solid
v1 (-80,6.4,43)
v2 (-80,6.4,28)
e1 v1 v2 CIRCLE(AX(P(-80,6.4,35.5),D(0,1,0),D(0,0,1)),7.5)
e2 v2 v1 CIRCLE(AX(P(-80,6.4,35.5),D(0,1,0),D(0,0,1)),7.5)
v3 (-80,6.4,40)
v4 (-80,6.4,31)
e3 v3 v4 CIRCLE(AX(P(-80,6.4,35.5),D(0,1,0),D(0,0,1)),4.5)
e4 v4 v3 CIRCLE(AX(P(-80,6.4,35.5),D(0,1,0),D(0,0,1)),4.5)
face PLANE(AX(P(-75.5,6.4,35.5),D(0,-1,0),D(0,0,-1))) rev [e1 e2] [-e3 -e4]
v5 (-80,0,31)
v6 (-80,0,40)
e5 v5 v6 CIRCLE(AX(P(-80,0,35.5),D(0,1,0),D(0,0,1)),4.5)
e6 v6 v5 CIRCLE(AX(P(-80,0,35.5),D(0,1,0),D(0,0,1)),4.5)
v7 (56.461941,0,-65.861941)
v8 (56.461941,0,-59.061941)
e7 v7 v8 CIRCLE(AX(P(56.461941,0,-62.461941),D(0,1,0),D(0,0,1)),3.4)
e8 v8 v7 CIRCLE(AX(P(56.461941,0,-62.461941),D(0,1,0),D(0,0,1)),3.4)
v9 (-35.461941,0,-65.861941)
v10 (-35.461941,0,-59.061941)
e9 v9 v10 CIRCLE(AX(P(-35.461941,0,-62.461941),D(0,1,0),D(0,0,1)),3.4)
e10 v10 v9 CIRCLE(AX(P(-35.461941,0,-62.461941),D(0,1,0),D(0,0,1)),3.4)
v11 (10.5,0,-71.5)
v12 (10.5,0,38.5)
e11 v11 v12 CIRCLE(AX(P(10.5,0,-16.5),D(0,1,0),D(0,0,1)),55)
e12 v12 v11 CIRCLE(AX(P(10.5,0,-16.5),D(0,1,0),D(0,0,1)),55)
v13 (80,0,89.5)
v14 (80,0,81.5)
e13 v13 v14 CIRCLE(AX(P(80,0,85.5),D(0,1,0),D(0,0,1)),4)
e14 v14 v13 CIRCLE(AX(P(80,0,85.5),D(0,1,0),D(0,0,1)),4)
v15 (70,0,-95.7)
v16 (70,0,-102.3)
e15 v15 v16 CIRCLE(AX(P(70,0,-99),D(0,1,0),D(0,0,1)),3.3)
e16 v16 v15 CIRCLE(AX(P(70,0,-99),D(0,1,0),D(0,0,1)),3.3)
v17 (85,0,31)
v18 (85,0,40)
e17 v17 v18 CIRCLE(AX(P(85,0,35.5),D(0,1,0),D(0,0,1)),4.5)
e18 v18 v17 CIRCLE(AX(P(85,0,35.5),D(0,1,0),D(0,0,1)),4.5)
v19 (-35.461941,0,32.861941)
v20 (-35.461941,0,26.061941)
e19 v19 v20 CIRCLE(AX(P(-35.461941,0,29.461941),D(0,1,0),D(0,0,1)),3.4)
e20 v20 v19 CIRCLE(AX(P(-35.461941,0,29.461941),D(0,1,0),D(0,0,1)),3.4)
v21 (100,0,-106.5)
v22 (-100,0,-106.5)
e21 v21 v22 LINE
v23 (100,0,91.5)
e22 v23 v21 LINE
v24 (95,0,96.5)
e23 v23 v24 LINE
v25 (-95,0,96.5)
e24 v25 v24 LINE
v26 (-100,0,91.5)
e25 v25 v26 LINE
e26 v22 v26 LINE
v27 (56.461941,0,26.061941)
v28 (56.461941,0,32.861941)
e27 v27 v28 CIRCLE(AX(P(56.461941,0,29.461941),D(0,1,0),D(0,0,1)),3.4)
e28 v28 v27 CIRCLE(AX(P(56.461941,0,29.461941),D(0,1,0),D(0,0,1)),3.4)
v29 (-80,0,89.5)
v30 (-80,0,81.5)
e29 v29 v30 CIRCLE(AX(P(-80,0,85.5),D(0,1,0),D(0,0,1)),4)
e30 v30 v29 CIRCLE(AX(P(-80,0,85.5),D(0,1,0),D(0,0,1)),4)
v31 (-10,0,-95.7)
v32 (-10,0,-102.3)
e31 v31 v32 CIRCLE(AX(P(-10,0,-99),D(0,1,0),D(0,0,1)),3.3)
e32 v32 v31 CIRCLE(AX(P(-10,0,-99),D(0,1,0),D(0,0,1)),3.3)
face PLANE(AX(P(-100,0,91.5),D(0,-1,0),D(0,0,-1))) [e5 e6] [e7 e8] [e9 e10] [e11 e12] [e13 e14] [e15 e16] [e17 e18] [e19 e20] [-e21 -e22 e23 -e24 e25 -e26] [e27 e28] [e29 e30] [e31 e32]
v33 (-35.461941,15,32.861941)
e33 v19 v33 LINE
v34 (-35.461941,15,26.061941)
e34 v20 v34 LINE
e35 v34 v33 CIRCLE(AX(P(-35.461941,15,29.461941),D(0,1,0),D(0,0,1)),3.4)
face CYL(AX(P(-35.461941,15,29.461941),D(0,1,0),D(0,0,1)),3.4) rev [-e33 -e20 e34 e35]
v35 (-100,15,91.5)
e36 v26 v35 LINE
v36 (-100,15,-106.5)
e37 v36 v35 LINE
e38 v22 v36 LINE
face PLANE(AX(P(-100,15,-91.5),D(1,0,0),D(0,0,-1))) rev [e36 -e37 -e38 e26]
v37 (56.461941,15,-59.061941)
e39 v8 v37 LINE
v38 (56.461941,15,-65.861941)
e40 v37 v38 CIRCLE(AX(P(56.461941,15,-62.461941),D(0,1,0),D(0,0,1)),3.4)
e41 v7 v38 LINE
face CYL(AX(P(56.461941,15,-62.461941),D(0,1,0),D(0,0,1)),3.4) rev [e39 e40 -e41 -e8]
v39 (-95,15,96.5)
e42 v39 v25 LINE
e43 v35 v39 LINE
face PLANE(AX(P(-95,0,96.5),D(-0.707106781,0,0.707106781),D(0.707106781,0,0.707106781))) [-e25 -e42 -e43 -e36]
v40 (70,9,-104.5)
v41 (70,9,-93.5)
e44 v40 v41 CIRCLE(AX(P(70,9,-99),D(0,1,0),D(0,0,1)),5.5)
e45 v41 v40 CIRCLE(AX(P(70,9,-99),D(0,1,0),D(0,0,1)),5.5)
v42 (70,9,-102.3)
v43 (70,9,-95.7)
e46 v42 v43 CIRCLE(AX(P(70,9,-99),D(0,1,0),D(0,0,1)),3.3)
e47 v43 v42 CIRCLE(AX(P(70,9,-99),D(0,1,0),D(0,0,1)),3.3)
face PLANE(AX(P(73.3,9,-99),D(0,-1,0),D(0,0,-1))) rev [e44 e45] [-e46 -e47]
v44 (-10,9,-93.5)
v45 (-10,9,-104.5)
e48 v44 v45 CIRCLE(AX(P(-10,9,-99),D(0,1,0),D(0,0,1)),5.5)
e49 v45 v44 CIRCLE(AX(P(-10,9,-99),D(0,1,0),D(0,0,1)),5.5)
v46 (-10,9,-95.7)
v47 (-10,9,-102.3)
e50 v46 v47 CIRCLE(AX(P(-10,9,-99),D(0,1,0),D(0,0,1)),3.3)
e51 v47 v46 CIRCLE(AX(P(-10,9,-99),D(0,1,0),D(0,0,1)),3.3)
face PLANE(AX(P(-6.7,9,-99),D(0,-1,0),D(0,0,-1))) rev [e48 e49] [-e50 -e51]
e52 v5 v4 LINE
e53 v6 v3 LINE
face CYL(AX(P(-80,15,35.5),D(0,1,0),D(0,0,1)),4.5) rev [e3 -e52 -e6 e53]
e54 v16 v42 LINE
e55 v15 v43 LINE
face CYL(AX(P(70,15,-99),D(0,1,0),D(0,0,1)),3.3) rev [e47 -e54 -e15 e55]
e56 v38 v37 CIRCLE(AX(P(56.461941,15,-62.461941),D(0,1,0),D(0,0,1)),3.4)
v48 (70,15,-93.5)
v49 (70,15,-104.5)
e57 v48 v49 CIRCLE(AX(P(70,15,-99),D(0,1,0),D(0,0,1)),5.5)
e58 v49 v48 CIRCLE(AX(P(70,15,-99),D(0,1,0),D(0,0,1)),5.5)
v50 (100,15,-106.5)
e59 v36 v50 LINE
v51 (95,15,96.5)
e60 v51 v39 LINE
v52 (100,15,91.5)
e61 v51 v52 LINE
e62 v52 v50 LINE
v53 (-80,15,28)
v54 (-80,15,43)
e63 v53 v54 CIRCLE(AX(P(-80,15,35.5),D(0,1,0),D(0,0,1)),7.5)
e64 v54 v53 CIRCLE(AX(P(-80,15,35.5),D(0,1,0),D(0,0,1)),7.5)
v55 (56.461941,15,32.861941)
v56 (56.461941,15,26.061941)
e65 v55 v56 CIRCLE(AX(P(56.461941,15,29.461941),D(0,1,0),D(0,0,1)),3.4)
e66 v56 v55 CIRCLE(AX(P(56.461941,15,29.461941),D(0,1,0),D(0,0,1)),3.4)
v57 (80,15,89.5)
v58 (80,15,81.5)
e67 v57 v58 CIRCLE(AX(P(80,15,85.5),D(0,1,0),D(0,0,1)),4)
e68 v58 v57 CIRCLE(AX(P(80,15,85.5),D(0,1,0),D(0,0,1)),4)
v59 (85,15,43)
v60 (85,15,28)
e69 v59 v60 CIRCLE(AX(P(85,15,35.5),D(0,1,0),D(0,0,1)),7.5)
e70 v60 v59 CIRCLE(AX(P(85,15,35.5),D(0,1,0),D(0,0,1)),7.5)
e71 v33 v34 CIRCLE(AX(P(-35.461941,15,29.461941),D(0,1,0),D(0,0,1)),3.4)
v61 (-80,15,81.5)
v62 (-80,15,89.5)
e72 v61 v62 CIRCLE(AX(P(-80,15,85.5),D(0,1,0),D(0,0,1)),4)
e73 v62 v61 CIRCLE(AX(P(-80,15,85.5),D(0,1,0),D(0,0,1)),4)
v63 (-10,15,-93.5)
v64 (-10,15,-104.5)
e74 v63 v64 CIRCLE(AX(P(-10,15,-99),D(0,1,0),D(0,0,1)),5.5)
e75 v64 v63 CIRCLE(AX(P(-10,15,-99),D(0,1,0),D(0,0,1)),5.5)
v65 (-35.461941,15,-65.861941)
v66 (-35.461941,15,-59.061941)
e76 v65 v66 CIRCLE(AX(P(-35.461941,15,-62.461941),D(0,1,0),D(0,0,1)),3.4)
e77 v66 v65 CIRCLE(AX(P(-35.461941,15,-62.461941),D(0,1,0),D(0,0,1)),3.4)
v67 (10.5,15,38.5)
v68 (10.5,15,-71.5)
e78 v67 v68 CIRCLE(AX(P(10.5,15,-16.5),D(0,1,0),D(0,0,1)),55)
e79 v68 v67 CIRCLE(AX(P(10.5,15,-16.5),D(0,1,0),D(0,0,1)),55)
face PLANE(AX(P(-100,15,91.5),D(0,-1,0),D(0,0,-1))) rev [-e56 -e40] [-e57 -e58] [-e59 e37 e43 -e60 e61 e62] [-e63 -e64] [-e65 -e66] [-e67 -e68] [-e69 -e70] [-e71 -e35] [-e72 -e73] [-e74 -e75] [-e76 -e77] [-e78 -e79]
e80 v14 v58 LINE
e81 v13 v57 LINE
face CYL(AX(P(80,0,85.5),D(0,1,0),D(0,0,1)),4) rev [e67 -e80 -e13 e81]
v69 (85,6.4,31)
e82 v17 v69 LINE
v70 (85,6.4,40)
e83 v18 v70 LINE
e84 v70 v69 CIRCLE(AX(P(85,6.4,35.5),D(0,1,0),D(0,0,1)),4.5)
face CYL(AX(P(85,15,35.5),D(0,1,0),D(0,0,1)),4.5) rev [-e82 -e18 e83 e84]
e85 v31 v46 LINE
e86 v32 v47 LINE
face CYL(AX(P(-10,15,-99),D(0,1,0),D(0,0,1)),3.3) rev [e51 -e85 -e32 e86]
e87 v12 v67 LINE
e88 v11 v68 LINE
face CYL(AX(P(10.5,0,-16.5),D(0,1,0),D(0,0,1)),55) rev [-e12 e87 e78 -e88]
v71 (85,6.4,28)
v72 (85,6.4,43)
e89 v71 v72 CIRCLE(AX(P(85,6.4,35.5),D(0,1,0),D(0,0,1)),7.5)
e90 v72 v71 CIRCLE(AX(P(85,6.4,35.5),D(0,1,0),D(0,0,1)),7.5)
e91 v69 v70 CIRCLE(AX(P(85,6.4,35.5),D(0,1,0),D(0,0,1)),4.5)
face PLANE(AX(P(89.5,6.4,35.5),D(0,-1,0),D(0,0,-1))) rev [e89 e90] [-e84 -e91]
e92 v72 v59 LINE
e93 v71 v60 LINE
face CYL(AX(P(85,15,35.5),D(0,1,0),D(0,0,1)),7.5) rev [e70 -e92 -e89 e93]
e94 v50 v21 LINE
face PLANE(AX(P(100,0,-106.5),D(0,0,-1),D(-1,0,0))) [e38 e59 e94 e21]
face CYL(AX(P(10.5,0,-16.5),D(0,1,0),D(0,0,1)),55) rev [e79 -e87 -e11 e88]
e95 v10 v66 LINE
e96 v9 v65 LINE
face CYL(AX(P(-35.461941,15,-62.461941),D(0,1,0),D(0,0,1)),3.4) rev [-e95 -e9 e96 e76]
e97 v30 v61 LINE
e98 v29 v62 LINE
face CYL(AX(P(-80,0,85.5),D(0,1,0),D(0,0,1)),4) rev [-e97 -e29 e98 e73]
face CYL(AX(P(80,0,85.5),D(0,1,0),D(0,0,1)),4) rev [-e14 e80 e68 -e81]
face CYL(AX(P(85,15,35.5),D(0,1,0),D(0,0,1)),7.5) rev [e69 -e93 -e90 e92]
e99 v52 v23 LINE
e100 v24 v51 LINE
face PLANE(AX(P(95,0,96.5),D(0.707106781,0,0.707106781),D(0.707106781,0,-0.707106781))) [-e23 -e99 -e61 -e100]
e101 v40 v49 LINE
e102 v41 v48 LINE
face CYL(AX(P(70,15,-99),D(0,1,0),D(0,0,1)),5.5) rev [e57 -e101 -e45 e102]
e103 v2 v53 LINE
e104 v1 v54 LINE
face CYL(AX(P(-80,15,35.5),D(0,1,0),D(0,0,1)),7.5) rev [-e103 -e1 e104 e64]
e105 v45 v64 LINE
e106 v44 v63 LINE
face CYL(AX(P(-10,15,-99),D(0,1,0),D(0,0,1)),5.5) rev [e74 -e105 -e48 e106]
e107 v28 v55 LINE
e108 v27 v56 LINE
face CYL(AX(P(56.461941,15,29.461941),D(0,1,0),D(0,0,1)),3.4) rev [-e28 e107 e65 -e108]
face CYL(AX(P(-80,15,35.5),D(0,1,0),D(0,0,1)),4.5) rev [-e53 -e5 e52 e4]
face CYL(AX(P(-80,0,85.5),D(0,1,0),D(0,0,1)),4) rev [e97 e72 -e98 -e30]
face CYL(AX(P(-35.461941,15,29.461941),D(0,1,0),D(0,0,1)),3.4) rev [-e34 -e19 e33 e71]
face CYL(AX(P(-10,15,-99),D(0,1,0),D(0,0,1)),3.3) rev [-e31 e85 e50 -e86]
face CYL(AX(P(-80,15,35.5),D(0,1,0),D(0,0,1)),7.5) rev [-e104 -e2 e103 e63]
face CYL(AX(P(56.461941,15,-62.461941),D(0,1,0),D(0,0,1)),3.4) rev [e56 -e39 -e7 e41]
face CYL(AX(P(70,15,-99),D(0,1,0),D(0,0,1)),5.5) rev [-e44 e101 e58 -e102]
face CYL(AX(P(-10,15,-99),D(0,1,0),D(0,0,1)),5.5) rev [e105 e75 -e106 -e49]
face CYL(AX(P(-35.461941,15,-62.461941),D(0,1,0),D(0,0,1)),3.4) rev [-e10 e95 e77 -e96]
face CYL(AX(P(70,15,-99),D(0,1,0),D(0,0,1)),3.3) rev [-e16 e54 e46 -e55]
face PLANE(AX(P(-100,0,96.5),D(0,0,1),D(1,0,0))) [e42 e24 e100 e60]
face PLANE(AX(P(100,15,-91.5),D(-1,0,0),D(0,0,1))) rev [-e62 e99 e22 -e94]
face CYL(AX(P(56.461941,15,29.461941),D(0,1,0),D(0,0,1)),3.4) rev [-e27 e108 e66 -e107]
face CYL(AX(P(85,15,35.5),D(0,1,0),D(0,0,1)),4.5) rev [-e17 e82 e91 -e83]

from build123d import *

# Parameters (mm, degrees)
SKETCH1_W                                           = 200
SKETCH1_H                                           = 183
BOSS_EXTRUDE1_DEPTH                                 = 15
M8_TAPPED_HOLE1_D                                   = 6.8
SKETCH11_W                                          = 200
SKETCH11_H                                          = 15
BOSS_EXTRUDE3_DEPTH                                 = 15
CBORE_FOR_M6_HEX_SOCKET_HEAD_CAP_SCREW1_D           = 6.6
CBORE_FOR_M6_HEX_SOCKET_HEAD_CAP_SCREW1_CBORE_D     = 11
CBORE_FOR_M6_HEX_SOCKET_HEAD_CAP_SCREW1_CBORE_DEPTH = 6
CBORE_FOR_M8_HEX_SOCKET_HEAD_CAP_SCREW1_D           = 9
CBORE_FOR_M8_HEX_SOCKET_HEAD_CAP_SCREW1_CBORE_D     = 15
CBORE_FOR_M8_HEX_SOCKET_HEAD_CAP_SCREW1_CBORE_DEPTH = 8.6
SKETCH9_W                                           = 200
SKETCH9_H                                           = 15
BOSS_EXTRUDE2_DEPTH                                 = 5
SKETCH10_R                                          = 4
CUT_EXTRUDE2_DEPTH                                  = 147.857924539
CHAMFER1_SIZE                                       = 5
SKETCH12_R                                          = 55
CUT_EXTRUDE3_DEPTH                                  = 147.857924539


with BuildPart() as part:
    # Sketch1 → Boss-Extrude1 (new body)
    with BuildSketch(Plane(origin=(0, 0, 0), x_dir=(1, 0, 0), z_dir=(0, 1, 0))):
        Rectangle(SKETCH1_W, SKETCH1_H)
    extrude(amount=BOSS_EXTRUDE1_DEPTH)

    # M8 Tapped Hole1 (through all)
    with Locations(Plane(origin=(0, 15, 0), x_dir=(-1, 0, 0), z_dir=(0, 1, 0))):
        with Locations((35.461940777, -62.461940777), (-56.461940777, -62.461940777), (35.461940777, 29.461940777), (-56.461940777, 29.461940777)):
            Hole(M8_TAPPED_HOLE1_D / 2)

    # Sketch11 → Boss-Extrude3 (add)
    with BuildSketch(Plane(origin=(0, 0, -91.5), x_dir=(-1, 0, 0), z_dir=(0, 0, -1))):
        with Locations((0, 7.5)):
            Rectangle(SKETCH11_W, SKETCH11_H)
    extrude(amount=BOSS_EXTRUDE3_DEPTH)

    # CBORE for M6 Hex Socket Head Cap Screw1 (through all)
    with Locations(Plane(origin=(0, 15, 0), x_dir=(-1, 0, 0), z_dir=(0, 1, 0))):
        with Locations((-70, -99), (10, -99)):
            CounterBoreHole(CBORE_FOR_M6_HEX_SOCKET_HEAD_CAP_SCREW1_D / 2, CBORE_FOR_M6_HEX_SOCKET_HEAD_CAP_SCREW1_CBORE_D / 2, CBORE_FOR_M6_HEX_SOCKET_HEAD_CAP_SCREW1_CBORE_DEPTH)

    # CBORE for M8 Hex Socket Head Cap Screw1 (through all)
    with Locations(Plane(origin=(0, 15, 0), x_dir=(-1, 0, 0), z_dir=(0, 1, 0))):
        with Locations((-85, 35.5), (80, 35.5)):
            CounterBoreHole(CBORE_FOR_M8_HEX_SOCKET_HEAD_CAP_SCREW1_D / 2, CBORE_FOR_M8_HEX_SOCKET_HEAD_CAP_SCREW1_CBORE_D / 2, CBORE_FOR_M8_HEX_SOCKET_HEAD_CAP_SCREW1_CBORE_DEPTH)

    # Sketch9 → Boss-Extrude2 (add)
    with BuildSketch(Plane.XY.offset(91.5)):
        with Locations((0, 7.5)):
            Rectangle(SKETCH9_W, SKETCH9_H)
    extrude(amount=BOSS_EXTRUDE2_DEPTH)

    # Sketch10 → Cut-Extrude2 (cut, through all)
    with BuildSketch(Plane(origin=(0, 15, 0), x_dir=(1, 0, 0), z_dir=(0, 1, 0))):
        with Locations(Location((-80, -85.5, 0), (0, 0, 270))):
            Circle(SKETCH10_R)
        with Locations(Location((80, -85.5, 0), (0, 0, 270))):
            Circle(SKETCH10_R)
    extrude(amount=-CUT_EXTRUDE2_DEPTH, mode=Mode.SUBTRACT)

    # Chamfer1
    chamfer1_edges = [part.edges().sort_by_distance(p)[0] for p in [
        (-100, 7.5, 96.5),
        (100, 7.5, 96.5),
    ]]
    chamfer(chamfer1_edges, length=CHAMFER1_SIZE)

    # Sketch12 → Cut-Extrude3 (cut, through all)
    with BuildSketch(Plane(origin=(0, 15, 0), x_dir=(1, 0, 0), z_dir=(0, 1, 0))):
        with Locations(Location((10.5, 16.5, 0), (0, 0, 270))):
            Circle(SKETCH12_R)
    extrude(amount=-CUT_EXTRUDE3_DEPTH, mode=Mode.SUBTRACT)


solid = part.part
